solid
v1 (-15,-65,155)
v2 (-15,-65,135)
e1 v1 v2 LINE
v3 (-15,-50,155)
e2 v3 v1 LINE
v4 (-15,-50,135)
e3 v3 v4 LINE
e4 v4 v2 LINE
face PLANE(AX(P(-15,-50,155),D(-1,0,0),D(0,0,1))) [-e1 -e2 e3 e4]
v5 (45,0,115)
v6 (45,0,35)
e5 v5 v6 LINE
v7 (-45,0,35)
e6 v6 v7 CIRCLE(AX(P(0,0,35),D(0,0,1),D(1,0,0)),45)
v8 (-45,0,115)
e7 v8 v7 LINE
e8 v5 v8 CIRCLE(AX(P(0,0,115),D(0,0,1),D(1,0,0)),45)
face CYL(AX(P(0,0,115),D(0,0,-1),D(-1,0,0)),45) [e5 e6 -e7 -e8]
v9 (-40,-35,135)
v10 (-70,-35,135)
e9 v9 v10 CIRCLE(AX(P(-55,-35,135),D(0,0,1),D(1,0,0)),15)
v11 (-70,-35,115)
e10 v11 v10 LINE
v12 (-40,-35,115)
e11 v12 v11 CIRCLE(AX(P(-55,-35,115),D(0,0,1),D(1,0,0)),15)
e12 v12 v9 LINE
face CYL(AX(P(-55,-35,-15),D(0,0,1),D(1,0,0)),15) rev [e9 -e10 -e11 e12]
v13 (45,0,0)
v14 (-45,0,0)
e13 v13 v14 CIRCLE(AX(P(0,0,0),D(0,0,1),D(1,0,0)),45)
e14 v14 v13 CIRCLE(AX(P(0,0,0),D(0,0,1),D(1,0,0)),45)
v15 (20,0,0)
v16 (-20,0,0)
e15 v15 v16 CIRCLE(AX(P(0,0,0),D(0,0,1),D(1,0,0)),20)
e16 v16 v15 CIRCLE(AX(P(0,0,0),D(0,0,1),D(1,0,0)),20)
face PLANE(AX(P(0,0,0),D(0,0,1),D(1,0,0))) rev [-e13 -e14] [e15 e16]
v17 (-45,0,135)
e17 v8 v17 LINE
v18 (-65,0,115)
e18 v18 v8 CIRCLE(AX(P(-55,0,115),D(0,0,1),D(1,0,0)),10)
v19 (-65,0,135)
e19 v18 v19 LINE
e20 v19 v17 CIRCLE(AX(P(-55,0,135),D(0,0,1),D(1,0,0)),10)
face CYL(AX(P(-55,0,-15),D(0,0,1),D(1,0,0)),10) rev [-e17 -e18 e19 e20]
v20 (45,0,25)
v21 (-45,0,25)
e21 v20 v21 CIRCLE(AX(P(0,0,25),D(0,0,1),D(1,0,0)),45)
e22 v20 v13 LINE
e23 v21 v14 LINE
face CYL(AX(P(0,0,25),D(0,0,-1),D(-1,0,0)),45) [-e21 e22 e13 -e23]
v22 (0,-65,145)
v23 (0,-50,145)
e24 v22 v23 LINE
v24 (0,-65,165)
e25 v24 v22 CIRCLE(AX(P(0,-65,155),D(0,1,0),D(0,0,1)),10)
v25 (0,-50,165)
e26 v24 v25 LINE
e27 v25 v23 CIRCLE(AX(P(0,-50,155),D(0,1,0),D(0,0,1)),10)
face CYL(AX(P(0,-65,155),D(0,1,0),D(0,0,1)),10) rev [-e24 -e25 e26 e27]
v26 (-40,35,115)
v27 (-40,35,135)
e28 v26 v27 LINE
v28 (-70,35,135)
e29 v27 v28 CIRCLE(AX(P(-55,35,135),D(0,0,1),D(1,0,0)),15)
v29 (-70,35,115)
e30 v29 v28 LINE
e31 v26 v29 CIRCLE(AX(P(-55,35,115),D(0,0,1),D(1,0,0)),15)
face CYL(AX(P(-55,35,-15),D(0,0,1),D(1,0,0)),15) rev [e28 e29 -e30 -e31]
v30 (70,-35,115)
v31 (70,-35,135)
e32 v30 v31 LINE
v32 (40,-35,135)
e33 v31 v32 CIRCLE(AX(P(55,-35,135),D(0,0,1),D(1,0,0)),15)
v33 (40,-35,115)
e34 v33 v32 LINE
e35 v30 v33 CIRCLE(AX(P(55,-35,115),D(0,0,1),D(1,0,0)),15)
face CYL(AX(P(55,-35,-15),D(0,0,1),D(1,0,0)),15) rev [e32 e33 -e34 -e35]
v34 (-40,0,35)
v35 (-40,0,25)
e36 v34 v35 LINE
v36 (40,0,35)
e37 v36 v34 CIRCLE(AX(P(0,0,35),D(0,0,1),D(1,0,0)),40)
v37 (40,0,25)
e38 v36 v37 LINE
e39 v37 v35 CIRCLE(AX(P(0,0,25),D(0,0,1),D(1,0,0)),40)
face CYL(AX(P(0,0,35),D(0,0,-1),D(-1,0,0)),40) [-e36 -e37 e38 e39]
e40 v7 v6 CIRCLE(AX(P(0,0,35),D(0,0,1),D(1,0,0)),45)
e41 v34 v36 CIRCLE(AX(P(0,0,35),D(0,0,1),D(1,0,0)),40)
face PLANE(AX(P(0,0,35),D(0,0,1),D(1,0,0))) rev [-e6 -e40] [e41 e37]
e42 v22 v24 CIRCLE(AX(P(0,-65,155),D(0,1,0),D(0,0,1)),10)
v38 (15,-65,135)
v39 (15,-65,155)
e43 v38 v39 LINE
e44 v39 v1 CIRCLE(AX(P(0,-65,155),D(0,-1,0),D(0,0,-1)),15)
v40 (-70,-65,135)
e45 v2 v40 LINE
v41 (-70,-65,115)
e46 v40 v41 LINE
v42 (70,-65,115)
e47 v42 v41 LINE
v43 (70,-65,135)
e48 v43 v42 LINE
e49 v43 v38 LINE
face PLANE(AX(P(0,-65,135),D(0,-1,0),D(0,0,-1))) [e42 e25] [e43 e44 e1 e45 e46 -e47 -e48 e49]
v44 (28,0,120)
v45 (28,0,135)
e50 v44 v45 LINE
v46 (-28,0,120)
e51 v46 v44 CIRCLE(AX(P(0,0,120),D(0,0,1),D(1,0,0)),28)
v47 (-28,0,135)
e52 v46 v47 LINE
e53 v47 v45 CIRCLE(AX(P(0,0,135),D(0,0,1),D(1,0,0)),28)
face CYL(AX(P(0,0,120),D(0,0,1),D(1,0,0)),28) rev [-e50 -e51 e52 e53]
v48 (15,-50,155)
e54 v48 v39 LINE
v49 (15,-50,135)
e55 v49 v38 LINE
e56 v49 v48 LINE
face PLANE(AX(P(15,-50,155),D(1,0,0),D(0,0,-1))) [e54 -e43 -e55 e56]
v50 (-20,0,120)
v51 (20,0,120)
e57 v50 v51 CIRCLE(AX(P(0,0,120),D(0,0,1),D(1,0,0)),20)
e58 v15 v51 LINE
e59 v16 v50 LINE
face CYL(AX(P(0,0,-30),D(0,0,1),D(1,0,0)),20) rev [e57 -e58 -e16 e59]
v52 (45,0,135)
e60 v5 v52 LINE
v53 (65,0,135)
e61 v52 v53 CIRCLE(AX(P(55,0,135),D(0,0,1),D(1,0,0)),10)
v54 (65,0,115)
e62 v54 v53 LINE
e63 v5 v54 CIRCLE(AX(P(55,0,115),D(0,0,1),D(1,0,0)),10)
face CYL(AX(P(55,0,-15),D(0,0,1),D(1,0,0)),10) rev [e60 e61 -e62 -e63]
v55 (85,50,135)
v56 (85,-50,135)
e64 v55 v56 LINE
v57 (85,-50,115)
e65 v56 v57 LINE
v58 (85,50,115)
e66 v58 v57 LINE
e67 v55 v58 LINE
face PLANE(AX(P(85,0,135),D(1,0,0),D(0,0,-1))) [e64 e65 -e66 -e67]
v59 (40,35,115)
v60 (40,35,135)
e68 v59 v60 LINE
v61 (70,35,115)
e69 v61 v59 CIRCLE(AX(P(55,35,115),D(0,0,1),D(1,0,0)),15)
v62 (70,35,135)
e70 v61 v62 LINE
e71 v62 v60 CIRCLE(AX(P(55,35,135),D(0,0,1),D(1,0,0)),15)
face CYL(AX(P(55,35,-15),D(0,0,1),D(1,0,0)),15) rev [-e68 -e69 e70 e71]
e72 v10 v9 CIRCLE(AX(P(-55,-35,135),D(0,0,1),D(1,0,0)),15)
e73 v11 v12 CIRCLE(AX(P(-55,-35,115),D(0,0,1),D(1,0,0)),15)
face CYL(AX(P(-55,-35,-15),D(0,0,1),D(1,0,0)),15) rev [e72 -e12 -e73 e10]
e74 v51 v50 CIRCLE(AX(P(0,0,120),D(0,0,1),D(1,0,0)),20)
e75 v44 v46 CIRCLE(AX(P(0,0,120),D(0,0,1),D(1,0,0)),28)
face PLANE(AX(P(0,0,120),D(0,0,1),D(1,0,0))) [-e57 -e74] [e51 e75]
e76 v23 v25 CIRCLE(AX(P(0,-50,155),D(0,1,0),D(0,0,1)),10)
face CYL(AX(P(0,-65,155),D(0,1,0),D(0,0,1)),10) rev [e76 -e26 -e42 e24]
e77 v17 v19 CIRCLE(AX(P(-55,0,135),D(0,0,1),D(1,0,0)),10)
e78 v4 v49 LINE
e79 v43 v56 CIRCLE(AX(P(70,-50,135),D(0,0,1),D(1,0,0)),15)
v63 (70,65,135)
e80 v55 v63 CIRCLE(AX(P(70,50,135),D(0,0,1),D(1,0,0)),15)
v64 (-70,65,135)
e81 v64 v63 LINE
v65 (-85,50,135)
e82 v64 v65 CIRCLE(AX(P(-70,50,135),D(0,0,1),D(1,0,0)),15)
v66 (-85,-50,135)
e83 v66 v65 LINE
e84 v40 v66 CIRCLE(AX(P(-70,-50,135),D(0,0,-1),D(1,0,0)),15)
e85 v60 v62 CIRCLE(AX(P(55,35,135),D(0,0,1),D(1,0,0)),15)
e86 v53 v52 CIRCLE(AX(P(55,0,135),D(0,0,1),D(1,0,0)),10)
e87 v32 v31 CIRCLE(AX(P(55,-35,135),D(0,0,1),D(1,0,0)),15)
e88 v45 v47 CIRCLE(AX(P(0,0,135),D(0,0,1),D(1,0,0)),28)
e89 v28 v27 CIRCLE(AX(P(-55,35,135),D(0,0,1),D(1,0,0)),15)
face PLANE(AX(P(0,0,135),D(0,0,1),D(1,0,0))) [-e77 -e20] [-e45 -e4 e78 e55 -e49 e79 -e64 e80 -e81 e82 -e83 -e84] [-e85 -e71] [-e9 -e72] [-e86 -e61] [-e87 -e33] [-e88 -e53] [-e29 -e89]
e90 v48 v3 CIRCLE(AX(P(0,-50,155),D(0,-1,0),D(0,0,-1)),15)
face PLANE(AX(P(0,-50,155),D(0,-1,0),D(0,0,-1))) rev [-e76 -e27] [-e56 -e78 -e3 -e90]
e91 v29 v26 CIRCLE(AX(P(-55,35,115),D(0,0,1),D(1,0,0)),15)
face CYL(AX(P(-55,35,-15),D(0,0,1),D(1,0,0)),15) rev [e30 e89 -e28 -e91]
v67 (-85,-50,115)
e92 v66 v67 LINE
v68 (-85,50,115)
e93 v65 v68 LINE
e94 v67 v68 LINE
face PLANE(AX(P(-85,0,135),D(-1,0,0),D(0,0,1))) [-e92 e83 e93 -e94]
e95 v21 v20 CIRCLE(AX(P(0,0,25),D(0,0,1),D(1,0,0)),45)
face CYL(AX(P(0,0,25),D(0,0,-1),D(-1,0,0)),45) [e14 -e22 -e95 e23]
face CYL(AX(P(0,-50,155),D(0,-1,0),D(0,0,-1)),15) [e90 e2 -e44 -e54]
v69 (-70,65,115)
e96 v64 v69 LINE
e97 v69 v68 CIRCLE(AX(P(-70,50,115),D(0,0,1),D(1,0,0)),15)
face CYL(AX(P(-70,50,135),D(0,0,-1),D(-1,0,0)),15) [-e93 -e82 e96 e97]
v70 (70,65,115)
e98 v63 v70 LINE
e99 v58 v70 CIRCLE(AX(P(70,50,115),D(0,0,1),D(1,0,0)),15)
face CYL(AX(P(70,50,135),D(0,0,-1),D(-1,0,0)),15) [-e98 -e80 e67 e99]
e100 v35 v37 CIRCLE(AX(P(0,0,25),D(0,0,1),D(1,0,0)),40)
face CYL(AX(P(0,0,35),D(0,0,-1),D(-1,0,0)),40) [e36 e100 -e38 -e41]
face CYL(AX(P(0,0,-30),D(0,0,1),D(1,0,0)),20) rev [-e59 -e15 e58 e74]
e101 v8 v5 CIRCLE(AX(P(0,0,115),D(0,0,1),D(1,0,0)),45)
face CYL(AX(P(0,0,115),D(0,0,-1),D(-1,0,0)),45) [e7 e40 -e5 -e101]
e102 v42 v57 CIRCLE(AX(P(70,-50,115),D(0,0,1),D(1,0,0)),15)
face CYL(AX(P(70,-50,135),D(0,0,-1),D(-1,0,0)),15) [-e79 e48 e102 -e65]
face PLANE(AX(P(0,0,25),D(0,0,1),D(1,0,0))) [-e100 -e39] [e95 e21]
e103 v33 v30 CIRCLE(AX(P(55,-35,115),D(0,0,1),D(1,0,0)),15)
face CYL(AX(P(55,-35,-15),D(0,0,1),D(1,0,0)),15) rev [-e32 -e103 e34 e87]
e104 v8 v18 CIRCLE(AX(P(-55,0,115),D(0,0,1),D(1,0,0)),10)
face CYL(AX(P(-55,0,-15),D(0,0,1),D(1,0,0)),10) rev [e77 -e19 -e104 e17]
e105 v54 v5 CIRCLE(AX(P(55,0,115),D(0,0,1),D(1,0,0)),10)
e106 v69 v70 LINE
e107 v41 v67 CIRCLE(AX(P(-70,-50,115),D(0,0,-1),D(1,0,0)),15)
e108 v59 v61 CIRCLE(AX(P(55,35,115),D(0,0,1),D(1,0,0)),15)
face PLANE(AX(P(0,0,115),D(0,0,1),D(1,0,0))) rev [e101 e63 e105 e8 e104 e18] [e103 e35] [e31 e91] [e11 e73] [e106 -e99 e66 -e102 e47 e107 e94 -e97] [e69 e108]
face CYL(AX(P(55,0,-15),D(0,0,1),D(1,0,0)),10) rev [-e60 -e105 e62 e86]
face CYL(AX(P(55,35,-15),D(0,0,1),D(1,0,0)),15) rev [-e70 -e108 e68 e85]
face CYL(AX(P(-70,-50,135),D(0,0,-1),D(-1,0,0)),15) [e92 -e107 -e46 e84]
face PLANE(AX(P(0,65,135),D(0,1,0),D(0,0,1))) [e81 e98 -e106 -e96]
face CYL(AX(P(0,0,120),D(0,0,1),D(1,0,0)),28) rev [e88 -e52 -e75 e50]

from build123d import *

# Parameters (mm, degrees)
COLUMN_BASE_SKETCH_R    = 45
COLUMN_BASE_90_DEPTH    = 25
GROOVE_NECK_SKETCH_R    = 40
GROOVE_NECK_80_DEPTH    = 10
COLUMN_BODY_SKETCH_R    = 45
COLUMN_BODY_90_DEPTH    = 80
TOP_PLATE_170X130_DEPTH = 20
BORE_STEP_SKETCH_R      = 28
BORE_STEP_28_DEPTH      = 15
COLUMN_BORE_SKETCH_R    = 20
COLUMN_BORE_40_DEPTH    = 150
PLATE_HOLES_SKETCH_R    = 15
PLATE_HOLES_SKETCH_R_2  = 10
PLATE_HOLES_6X_DEPTH    = 150
EYE_LUG_DEPTH           = 15
LUG_HOLE_SKETCH_R       = 10
LUG_HOLE_10_DEPTH       = 15


with BuildPart() as part:
    # Column Base Sketch → Column Base Ø90 (new body)
    with BuildSketch(Plane.XY):
        Circle(COLUMN_BASE_SKETCH_R)
    extrude(amount=COLUMN_BASE_90_DEPTH)

    # Groove Neck Sketch → Groove Neck Ø80 (add)
    with BuildSketch(Plane.XY.offset(25)):
        Circle(GROOVE_NECK_SKETCH_R)
    extrude(amount=GROOVE_NECK_80_DEPTH)

    # Column Body Sketch → Column Body Ø90 (add)
    with BuildSketch(Plane.XY.offset(35)):
        Circle(COLUMN_BODY_SKETCH_R)
    extrude(amount=COLUMN_BODY_90_DEPTH)

    # Top Plate Sketch → Top Plate 170x130 (add)
    with BuildSketch(Plane.XY.offset(115)):
        with BuildLine():
            Line((70, 65), (0, 65))
            Line((0, 65), (-70, 65))
            ThreePointArc((-70, 65), (-80.606601718, 60.606601718), (-85, 50))
            Line((-85, 50), (-85, -50))
            ThreePointArc((-85, -50), (-80.606601718, -60.606601718), (-70, -65))
            Line((-70, -65), (70, -65))
            ThreePointArc((70, -65), (80.606601718, -60.606601718), (85, -50))
            Line((85, -50), (85, 50))
            ThreePointArc((85, 50), (80.606601718, 60.606601718), (70, 65))
        make_face()
    extrude(amount=TOP_PLATE_170X130_DEPTH)

    # Bore Step Sketch → Bore Step Ø28 (cut)
    with BuildSketch(Plane.XY.offset(135)):
        Circle(BORE_STEP_SKETCH_R)
    extrude(amount=-BORE_STEP_28_DEPTH, mode=Mode.SUBTRACT)

    # Column Bore Sketch → Column Bore Ø40 (cut)
    with BuildSketch(Plane.XY.offset(120)):
        Circle(COLUMN_BORE_SKETCH_R)
    extrude(amount=-COLUMN_BORE_40_DEPTH, mode=Mode.SUBTRACT)

    # Plate Holes Sketch → Plate Holes 6x (cut)
    with BuildSketch(Plane.XY.offset(135)):
        with Locations((-55, 35)):
            Circle(PLATE_HOLES_SKETCH_R)
        with Locations((55, 35)):
            Circle(PLATE_HOLES_SKETCH_R)
        with Locations((-55, -35)):
            Circle(PLATE_HOLES_SKETCH_R)
        with Locations((55, -35)):
            Circle(PLATE_HOLES_SKETCH_R)
        with Locations((-55, 0)):
            Circle(PLATE_HOLES_SKETCH_R_2)
        with Locations((55, 0)):
            Circle(PLATE_HOLES_SKETCH_R_2)
    extrude(amount=-PLATE_HOLES_6X_DEPTH, mode=Mode.SUBTRACT)

    # Eye Lug Sketch → Eye Lug (add)
    with BuildSketch(Plane.XZ.offset(65)):
        with BuildLine():
            Line((-15, 135), (15, 135))
            Line((15, 135), (15, 155))
            ThreePointArc((15, 155), (0, 170), (-15, 155))
            Line((-15, 155), (-15, 135))
        make_face()
    extrude(amount=-EYE_LUG_DEPTH)

    # Lug Hole Sketch → Lug Hole Ø10 (cut)
    with BuildSketch(Plane(origin=(0, -50, 0), x_dir=(1, 0, 0), z_dir=(0, 1, 0))):
        with Locations(Location((0, -155, 0), (0, 0, 270))):
            Circle(LUG_HOLE_SKETCH_R)
    extrude(amount=-LUG_HOLE_10_DEPTH, mode=Mode.SUBTRACT)


solid = part.part
